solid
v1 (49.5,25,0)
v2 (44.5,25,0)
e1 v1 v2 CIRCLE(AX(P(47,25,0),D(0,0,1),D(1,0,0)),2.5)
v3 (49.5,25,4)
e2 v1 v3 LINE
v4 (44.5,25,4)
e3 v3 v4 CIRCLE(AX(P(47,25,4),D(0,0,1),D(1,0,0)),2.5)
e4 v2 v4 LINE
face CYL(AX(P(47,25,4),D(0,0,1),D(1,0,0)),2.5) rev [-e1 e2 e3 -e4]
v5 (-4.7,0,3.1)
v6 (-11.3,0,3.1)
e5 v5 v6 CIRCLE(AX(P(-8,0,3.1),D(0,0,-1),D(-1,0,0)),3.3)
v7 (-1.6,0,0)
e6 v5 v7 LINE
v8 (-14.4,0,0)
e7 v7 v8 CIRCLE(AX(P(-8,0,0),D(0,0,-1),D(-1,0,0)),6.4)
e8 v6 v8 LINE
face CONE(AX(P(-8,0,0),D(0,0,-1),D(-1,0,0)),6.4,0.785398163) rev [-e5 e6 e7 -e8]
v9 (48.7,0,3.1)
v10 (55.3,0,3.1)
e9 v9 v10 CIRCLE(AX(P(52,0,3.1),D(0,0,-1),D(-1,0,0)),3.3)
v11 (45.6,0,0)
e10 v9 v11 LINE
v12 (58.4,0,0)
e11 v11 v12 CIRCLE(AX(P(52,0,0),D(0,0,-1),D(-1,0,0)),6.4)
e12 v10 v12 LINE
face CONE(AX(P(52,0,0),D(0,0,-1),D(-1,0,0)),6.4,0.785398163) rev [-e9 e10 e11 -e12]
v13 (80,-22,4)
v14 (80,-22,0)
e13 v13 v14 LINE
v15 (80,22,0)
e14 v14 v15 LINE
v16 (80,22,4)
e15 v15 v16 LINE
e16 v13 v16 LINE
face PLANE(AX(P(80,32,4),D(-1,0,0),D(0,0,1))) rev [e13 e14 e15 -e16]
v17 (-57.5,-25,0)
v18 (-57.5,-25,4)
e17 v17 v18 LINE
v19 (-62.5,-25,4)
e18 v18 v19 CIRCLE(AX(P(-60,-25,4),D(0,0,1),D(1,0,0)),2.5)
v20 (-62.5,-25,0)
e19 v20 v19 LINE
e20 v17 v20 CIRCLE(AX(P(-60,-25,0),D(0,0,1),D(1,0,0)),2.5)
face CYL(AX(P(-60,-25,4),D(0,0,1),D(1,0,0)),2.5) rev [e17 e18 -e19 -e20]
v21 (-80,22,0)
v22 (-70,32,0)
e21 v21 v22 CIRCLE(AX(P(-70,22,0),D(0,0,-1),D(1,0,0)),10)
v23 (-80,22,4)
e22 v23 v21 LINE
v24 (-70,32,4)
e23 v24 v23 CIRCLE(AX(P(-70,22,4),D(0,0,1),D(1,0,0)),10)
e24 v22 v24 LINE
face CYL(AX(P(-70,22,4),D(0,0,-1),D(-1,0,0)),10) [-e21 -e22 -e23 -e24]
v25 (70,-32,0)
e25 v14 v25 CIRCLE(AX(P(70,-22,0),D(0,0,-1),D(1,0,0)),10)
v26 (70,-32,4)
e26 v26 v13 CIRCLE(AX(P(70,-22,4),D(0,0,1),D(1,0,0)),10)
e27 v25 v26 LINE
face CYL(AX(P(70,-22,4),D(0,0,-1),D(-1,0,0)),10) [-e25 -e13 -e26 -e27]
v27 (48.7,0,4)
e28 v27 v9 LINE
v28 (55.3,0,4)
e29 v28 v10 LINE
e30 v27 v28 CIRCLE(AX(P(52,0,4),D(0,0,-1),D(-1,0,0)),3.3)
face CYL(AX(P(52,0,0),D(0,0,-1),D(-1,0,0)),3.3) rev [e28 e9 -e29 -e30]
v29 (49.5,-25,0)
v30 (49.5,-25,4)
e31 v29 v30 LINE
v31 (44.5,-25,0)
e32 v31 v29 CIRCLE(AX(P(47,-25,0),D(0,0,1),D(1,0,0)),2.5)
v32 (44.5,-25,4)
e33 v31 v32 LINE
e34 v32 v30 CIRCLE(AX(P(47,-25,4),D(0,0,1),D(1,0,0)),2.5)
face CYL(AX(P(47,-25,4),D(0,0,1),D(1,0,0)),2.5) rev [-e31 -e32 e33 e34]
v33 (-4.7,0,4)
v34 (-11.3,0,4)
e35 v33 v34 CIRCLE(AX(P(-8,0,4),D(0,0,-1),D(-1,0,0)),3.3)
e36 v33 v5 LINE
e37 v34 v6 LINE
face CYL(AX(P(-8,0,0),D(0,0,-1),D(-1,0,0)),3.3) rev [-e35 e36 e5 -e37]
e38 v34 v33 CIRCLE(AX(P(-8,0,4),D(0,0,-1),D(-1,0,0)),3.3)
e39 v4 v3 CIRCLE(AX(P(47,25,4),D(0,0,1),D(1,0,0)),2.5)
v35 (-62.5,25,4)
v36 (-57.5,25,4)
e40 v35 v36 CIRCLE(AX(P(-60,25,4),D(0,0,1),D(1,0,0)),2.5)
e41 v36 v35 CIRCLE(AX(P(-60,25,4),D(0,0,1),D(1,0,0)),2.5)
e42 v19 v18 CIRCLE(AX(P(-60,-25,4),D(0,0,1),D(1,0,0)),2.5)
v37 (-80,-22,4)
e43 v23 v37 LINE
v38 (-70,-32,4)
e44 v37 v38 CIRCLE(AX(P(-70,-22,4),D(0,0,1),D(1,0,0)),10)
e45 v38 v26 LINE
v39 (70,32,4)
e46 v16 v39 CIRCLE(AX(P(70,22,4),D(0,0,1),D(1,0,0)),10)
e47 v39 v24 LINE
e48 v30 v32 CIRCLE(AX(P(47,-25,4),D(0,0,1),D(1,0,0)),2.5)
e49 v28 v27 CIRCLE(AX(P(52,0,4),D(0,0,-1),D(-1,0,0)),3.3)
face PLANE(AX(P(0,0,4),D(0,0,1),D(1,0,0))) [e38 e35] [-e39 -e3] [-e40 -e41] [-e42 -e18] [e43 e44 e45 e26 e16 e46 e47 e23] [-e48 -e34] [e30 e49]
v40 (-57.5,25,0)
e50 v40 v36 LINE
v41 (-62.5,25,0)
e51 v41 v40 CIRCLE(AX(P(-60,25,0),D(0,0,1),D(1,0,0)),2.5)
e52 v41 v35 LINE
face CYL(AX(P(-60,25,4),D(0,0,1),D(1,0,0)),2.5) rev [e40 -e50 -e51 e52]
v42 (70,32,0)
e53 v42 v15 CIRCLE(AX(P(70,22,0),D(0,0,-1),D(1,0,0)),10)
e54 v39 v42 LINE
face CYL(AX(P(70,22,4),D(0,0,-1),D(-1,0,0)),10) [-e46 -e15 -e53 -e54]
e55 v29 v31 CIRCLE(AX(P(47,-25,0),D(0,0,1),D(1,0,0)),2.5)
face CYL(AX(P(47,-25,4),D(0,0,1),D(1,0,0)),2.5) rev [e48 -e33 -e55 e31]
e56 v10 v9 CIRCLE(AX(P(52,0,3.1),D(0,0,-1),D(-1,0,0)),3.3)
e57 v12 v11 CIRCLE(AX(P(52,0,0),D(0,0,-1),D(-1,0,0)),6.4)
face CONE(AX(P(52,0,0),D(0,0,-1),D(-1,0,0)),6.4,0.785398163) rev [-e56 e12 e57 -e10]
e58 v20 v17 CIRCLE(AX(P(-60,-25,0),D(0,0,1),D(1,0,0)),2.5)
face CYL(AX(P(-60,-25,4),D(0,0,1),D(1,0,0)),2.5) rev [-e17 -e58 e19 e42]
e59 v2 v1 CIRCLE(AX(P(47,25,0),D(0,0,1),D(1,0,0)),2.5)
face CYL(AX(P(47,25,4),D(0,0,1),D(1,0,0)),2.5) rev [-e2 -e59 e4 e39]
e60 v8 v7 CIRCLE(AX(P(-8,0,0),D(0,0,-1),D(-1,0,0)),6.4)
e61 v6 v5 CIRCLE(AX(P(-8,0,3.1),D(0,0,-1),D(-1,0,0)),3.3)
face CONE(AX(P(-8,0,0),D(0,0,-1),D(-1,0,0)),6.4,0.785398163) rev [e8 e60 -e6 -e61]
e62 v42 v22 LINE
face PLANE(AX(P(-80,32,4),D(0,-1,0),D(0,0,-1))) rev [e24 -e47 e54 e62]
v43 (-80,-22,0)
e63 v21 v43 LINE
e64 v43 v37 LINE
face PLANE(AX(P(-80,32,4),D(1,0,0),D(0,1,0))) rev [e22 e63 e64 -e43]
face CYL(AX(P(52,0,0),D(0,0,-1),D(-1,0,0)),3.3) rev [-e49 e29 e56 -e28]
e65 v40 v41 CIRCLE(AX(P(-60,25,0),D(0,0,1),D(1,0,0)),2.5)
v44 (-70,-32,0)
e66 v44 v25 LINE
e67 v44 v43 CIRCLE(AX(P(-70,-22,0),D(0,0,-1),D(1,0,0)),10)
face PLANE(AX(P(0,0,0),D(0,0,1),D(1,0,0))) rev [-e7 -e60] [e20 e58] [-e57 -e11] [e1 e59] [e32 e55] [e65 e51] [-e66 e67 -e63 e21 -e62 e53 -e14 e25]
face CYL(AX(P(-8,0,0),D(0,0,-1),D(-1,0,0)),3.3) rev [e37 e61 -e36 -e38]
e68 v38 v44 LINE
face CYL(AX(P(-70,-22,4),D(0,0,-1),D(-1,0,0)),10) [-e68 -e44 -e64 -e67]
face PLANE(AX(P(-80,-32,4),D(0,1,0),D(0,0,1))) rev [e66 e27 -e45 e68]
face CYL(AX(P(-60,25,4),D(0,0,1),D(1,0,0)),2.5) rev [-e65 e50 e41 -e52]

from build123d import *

# Parameters (mm, degrees)
SKETCH_1_W               = 160
SKETCH_1_H               = 64
EXTRUDE_1_DEPTH          = 4
FILLET_1_R               = 10
HOLE_WIZARD_M6_1_D       = 5
HOLE_WIZARD_2_AT_2_COUNT = 2
HOLE_WIZARD_2_AT_2_PITCH = 60


with BuildPart() as part:
    # 草图1 → 凸台-拉伸1 (new body)
    with BuildSketch(Plane.XY):
        Rectangle(SKETCH_1_W, SKETCH_1_H)
    extrude(amount=EXTRUDE_1_DEPTH)

    # 圆角1
    fillet_1_edges = [part.edges().sort_by_distance(p)[0] for p in [
        (80, -32, 2),
        (-80, -32, 2),
        (-80, 32, 2),
        (80, 32, 2),
    ]]
    fillet(fillet_1_edges, radius=FILLET_1_R)

    # M6 螺纹孔1 (through all)
    with Locations(Plane.XY.offset(4)):
        with Locations((-60, 25), (-60, -25), (47, 25), (47, -25)):
            Hole(HOLE_WIZARD_M6_1_D / 2)

    # 草图6 → 打孔尺寸(%根据)内六角花形半沉头螺钉的类型2 (revolve, cut)
    with BuildSketch(Plane.YZ.offset(52)):
        Polygon((0, 0), (0, 4), (3.3, 4), (3.3, 3.1), (6.4, 0), align=None)
    hole_wizard_2 = revolve(axis=Axis((52, 0, -6.35), (0, 0, 1)), mode=Mode.SUBTRACT)

    # 打孔尺寸(%根据)内六角花形半沉头螺钉的类型2 at 2: 打孔尺寸(%根据)内六角花形半沉头螺钉的类型2 ×2
    with Locations(*[(-i * HOLE_WIZARD_2_AT_2_PITCH, 0, 0) for i in range(1, HOLE_WIZARD_2_AT_2_COUNT)]):
        add(hole_wizard_2, mode=Mode.SUBTRACT)


solid = part.part
